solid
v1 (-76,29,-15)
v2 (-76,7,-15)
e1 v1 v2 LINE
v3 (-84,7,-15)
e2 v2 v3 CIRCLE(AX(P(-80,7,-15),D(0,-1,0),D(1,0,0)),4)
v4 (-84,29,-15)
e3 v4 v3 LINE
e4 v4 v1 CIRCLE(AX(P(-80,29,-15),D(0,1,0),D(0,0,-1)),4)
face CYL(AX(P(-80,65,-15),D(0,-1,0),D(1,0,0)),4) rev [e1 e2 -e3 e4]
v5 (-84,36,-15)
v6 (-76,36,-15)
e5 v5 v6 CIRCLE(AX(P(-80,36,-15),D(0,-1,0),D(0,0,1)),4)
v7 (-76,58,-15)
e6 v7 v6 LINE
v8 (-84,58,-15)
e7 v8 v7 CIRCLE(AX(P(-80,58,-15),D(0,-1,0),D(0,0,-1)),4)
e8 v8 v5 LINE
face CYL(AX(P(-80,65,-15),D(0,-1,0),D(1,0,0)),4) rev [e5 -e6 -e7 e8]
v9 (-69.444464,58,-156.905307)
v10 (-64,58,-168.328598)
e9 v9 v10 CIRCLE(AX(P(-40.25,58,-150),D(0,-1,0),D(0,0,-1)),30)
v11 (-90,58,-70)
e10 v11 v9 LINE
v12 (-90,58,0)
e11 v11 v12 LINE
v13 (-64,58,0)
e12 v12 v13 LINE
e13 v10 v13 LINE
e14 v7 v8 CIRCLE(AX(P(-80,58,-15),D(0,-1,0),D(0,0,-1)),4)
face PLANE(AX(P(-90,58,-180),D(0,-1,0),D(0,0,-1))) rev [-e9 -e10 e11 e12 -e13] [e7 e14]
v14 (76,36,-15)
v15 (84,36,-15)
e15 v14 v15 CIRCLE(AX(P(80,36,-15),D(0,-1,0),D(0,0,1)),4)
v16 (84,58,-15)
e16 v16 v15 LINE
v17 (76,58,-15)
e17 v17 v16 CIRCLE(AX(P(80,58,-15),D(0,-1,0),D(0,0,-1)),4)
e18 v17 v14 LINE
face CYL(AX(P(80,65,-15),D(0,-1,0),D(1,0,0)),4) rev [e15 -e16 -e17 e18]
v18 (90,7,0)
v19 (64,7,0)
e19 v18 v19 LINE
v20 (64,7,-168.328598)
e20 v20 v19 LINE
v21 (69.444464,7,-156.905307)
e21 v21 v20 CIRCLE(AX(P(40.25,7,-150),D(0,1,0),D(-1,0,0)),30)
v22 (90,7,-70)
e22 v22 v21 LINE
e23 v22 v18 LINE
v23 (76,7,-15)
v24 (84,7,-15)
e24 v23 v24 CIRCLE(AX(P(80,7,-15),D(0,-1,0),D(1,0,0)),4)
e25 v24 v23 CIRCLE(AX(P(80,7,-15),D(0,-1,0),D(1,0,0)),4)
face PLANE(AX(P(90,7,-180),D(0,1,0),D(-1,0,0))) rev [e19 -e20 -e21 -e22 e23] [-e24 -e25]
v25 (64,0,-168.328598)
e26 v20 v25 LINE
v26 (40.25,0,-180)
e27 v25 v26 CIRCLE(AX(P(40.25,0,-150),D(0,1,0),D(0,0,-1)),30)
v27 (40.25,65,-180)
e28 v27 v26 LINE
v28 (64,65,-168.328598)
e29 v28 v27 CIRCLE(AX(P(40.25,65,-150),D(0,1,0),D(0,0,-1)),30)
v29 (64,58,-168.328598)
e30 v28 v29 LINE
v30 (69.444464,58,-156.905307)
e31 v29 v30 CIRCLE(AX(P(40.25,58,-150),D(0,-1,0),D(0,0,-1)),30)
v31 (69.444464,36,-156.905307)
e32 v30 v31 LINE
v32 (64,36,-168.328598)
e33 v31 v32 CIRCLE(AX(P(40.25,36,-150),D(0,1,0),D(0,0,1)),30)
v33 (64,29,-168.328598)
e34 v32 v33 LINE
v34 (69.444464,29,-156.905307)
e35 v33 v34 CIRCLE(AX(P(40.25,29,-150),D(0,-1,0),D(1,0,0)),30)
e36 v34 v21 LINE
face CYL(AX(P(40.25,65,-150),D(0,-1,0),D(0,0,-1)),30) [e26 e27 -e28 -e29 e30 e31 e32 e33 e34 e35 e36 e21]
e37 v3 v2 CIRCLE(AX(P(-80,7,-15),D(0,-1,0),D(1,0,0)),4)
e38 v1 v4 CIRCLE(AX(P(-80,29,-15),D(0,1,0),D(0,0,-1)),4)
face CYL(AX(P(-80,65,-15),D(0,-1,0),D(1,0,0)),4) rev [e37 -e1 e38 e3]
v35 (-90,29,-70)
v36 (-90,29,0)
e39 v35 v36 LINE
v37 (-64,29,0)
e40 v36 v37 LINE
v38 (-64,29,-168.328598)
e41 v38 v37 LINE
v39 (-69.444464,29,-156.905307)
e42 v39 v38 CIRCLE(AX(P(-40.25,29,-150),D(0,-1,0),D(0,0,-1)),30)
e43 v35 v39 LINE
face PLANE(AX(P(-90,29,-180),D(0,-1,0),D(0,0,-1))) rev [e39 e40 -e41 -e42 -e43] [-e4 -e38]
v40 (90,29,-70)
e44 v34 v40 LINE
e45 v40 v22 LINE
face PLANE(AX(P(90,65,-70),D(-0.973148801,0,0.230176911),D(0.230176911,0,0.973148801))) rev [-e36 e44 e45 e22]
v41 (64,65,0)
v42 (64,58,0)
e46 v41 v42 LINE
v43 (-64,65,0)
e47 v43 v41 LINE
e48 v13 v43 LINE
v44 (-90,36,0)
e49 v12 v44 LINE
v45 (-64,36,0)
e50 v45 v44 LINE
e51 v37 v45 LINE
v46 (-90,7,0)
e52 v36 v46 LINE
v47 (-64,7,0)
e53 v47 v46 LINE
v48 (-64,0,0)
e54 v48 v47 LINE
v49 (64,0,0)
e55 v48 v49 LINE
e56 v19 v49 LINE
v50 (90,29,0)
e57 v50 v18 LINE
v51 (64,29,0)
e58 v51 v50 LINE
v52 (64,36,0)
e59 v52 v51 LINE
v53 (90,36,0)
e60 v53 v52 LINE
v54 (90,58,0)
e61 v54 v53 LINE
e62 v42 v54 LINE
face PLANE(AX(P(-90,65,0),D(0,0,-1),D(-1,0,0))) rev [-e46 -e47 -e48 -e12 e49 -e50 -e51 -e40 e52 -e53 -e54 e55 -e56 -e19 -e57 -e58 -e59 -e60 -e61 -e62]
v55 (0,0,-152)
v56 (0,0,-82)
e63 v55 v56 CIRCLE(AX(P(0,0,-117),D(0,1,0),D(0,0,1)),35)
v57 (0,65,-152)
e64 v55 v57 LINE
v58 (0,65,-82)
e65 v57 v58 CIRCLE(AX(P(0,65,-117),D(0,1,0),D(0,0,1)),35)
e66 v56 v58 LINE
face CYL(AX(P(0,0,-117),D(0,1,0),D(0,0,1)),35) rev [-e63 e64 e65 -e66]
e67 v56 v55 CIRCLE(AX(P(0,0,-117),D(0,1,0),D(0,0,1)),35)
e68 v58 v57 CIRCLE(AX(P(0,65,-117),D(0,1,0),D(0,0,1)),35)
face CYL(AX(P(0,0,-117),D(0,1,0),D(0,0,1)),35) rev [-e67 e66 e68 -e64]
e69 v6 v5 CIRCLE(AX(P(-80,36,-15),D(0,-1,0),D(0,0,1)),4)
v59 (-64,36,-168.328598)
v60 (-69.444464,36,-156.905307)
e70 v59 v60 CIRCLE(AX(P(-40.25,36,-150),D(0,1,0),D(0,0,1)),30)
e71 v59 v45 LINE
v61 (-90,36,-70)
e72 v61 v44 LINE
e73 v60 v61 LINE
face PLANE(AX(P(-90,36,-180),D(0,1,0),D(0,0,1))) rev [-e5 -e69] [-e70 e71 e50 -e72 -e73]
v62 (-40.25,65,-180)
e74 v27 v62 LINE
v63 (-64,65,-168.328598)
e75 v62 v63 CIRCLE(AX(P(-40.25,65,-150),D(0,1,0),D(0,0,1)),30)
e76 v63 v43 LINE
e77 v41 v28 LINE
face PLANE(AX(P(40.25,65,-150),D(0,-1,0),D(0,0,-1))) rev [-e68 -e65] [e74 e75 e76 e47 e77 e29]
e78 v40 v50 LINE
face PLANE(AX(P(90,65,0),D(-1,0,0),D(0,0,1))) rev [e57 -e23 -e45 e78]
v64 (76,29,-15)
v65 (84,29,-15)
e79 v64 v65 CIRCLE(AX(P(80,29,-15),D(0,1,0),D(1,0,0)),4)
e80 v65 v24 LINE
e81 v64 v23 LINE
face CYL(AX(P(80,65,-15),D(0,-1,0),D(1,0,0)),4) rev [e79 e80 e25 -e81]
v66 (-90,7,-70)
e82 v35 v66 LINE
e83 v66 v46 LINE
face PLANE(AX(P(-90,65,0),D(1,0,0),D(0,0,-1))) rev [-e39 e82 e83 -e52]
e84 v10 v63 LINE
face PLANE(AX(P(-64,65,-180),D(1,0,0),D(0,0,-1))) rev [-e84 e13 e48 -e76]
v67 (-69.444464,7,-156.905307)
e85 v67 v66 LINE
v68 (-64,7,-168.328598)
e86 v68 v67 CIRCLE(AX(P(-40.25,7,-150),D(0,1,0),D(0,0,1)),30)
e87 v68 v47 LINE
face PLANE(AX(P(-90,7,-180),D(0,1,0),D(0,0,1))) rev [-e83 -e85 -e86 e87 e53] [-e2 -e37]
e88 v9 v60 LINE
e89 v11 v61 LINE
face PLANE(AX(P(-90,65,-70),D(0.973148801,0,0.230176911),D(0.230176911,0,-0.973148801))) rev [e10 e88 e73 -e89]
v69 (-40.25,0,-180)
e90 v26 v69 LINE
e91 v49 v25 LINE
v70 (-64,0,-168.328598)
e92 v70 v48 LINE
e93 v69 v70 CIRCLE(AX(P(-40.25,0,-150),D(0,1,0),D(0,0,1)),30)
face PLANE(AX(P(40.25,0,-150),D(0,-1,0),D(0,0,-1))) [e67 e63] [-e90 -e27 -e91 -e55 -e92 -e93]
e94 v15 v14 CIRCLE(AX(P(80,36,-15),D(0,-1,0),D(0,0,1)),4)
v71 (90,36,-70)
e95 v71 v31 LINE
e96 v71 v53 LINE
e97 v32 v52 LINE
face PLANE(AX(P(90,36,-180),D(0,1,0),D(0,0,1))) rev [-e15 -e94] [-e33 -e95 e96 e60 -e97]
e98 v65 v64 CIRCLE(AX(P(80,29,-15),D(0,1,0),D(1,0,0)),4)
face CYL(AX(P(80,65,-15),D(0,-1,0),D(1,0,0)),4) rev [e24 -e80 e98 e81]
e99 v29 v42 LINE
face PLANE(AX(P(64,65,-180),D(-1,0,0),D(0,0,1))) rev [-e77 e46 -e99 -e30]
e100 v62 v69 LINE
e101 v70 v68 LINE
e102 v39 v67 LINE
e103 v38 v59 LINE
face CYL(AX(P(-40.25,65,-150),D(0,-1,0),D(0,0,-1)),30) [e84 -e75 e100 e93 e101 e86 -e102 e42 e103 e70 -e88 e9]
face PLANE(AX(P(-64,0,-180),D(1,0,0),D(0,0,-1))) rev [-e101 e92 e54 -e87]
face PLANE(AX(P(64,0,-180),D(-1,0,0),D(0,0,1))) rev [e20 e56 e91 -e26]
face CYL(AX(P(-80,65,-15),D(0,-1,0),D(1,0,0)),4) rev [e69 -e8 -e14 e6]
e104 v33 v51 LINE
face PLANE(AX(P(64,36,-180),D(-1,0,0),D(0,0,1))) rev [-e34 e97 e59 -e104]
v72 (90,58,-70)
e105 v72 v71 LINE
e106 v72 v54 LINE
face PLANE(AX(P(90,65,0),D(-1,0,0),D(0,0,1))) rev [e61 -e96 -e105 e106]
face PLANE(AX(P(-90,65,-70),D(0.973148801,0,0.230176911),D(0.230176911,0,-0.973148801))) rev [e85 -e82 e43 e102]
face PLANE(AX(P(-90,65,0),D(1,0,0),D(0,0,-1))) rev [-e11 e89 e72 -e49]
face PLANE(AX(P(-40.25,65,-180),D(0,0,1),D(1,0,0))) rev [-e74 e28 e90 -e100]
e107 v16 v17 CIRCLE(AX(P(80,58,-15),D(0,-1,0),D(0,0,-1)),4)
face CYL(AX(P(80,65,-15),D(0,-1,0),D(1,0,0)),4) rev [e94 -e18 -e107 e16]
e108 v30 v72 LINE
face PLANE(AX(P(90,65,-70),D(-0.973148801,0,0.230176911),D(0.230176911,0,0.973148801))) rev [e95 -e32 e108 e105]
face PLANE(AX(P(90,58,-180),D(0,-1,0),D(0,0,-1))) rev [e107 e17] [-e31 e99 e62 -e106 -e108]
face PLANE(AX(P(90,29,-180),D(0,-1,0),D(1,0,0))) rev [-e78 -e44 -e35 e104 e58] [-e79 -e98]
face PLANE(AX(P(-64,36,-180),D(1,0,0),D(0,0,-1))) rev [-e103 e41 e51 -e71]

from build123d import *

# Parameters (mm, degrees)
BOSS_EXTRUDE1_DEPTH = 65
SKETCH2_R           = 35
CUT_EXTRUDE1_DEPTH  = 65
SKETCH3_W           = 26
SKETCH3_H           = 7
CUT_EXTRUDE2_DEPTH  = 212.482859826
SKETCH4_R           = 4
CUT_EXTRUDE3_DEPTH  = 210.437341465
SKETCH5_W           = 26
SKETCH5_H           = 7
CUT_EXTRUDE4_DEPTH  = 212.482859826


with BuildPart() as part:
    # Sketch1 → Boss-Extrude1 (new body)
    with BuildSketch(Plane(origin=(0, 0, 0), x_dir=(1, 0, 0), z_dir=(0, 1, 0))):
        with BuildLine():
            Line((-90, 0), (90, 0))
            Line((90, 0), (90, 70))
            Line((90, 70), (69.444464042, 156.905307326))
            ThreePointArc((69.444464042, 156.905307326), (58.862371963, 173.528272565), (40.25, 180))
            Line((40.25, 180), (-40.25, 180))
            ThreePointArc((-40.25, 180), (-58.862371963, 173.528272565), (-69.444464042, 156.905307326))
            Line((-69.444464042, 156.905307326), (-90, 70))
            Line((-90, 70), (-90, 0))
        make_face()
    extrude(amount=BOSS_EXTRUDE1_DEPTH)

    # Sketch2 → Cut-Extrude1 (cut)
    with BuildSketch(Plane(origin=(0, 65, 0), x_dir=(1, 0, 0), z_dir=(0, 1, 0))):
        with Locations(Location((0, 117, 0), (0, 0, 270))):
            Circle(SKETCH2_R)
    extrude(amount=-CUT_EXTRUDE1_DEPTH, mode=Mode.SUBTRACT)

    # Sketch3 → Cut-Extrude2 (cut, through all)
    with BuildSketch(Plane.XY):
        with Locations((77, 3.5)):
            Rectangle(SKETCH3_W, SKETCH3_H)
        with Locations((77, 61.5)):
            Rectangle(SKETCH3_W, SKETCH3_H)
        with Locations((-77, 61.5)):
            Rectangle(SKETCH3_W, SKETCH3_H)
        with Locations((-77, 3.5)):
            Rectangle(SKETCH3_W, SKETCH3_H)
    extrude(amount=-CUT_EXTRUDE2_DEPTH, mode=Mode.SUBTRACT)

    # Sketch4 → Cut-Extrude3 (cut, through all)
    with BuildSketch(Plane.XZ.offset(-7)):
        with Locations((80, -15)):
            Circle(SKETCH4_R)
        with Locations((-80, -15)):
            Circle(SKETCH4_R)
    extrude(amount=-CUT_EXTRUDE3_DEPTH, mode=Mode.SUBTRACT)

    # Sketch5 → Cut-Extrude4 (cut, through all)
    with BuildSketch(Plane.XY):
        with Locations((-77, 32.5)):
            Rectangle(SKETCH5_W, SKETCH5_H)
        with Locations((77, 32.5)):
            Rectangle(SKETCH5_W, SKETCH5_H)
    extrude(amount=-CUT_EXTRUDE4_DEPTH, mode=Mode.SUBTRACT)


solid = part.part
